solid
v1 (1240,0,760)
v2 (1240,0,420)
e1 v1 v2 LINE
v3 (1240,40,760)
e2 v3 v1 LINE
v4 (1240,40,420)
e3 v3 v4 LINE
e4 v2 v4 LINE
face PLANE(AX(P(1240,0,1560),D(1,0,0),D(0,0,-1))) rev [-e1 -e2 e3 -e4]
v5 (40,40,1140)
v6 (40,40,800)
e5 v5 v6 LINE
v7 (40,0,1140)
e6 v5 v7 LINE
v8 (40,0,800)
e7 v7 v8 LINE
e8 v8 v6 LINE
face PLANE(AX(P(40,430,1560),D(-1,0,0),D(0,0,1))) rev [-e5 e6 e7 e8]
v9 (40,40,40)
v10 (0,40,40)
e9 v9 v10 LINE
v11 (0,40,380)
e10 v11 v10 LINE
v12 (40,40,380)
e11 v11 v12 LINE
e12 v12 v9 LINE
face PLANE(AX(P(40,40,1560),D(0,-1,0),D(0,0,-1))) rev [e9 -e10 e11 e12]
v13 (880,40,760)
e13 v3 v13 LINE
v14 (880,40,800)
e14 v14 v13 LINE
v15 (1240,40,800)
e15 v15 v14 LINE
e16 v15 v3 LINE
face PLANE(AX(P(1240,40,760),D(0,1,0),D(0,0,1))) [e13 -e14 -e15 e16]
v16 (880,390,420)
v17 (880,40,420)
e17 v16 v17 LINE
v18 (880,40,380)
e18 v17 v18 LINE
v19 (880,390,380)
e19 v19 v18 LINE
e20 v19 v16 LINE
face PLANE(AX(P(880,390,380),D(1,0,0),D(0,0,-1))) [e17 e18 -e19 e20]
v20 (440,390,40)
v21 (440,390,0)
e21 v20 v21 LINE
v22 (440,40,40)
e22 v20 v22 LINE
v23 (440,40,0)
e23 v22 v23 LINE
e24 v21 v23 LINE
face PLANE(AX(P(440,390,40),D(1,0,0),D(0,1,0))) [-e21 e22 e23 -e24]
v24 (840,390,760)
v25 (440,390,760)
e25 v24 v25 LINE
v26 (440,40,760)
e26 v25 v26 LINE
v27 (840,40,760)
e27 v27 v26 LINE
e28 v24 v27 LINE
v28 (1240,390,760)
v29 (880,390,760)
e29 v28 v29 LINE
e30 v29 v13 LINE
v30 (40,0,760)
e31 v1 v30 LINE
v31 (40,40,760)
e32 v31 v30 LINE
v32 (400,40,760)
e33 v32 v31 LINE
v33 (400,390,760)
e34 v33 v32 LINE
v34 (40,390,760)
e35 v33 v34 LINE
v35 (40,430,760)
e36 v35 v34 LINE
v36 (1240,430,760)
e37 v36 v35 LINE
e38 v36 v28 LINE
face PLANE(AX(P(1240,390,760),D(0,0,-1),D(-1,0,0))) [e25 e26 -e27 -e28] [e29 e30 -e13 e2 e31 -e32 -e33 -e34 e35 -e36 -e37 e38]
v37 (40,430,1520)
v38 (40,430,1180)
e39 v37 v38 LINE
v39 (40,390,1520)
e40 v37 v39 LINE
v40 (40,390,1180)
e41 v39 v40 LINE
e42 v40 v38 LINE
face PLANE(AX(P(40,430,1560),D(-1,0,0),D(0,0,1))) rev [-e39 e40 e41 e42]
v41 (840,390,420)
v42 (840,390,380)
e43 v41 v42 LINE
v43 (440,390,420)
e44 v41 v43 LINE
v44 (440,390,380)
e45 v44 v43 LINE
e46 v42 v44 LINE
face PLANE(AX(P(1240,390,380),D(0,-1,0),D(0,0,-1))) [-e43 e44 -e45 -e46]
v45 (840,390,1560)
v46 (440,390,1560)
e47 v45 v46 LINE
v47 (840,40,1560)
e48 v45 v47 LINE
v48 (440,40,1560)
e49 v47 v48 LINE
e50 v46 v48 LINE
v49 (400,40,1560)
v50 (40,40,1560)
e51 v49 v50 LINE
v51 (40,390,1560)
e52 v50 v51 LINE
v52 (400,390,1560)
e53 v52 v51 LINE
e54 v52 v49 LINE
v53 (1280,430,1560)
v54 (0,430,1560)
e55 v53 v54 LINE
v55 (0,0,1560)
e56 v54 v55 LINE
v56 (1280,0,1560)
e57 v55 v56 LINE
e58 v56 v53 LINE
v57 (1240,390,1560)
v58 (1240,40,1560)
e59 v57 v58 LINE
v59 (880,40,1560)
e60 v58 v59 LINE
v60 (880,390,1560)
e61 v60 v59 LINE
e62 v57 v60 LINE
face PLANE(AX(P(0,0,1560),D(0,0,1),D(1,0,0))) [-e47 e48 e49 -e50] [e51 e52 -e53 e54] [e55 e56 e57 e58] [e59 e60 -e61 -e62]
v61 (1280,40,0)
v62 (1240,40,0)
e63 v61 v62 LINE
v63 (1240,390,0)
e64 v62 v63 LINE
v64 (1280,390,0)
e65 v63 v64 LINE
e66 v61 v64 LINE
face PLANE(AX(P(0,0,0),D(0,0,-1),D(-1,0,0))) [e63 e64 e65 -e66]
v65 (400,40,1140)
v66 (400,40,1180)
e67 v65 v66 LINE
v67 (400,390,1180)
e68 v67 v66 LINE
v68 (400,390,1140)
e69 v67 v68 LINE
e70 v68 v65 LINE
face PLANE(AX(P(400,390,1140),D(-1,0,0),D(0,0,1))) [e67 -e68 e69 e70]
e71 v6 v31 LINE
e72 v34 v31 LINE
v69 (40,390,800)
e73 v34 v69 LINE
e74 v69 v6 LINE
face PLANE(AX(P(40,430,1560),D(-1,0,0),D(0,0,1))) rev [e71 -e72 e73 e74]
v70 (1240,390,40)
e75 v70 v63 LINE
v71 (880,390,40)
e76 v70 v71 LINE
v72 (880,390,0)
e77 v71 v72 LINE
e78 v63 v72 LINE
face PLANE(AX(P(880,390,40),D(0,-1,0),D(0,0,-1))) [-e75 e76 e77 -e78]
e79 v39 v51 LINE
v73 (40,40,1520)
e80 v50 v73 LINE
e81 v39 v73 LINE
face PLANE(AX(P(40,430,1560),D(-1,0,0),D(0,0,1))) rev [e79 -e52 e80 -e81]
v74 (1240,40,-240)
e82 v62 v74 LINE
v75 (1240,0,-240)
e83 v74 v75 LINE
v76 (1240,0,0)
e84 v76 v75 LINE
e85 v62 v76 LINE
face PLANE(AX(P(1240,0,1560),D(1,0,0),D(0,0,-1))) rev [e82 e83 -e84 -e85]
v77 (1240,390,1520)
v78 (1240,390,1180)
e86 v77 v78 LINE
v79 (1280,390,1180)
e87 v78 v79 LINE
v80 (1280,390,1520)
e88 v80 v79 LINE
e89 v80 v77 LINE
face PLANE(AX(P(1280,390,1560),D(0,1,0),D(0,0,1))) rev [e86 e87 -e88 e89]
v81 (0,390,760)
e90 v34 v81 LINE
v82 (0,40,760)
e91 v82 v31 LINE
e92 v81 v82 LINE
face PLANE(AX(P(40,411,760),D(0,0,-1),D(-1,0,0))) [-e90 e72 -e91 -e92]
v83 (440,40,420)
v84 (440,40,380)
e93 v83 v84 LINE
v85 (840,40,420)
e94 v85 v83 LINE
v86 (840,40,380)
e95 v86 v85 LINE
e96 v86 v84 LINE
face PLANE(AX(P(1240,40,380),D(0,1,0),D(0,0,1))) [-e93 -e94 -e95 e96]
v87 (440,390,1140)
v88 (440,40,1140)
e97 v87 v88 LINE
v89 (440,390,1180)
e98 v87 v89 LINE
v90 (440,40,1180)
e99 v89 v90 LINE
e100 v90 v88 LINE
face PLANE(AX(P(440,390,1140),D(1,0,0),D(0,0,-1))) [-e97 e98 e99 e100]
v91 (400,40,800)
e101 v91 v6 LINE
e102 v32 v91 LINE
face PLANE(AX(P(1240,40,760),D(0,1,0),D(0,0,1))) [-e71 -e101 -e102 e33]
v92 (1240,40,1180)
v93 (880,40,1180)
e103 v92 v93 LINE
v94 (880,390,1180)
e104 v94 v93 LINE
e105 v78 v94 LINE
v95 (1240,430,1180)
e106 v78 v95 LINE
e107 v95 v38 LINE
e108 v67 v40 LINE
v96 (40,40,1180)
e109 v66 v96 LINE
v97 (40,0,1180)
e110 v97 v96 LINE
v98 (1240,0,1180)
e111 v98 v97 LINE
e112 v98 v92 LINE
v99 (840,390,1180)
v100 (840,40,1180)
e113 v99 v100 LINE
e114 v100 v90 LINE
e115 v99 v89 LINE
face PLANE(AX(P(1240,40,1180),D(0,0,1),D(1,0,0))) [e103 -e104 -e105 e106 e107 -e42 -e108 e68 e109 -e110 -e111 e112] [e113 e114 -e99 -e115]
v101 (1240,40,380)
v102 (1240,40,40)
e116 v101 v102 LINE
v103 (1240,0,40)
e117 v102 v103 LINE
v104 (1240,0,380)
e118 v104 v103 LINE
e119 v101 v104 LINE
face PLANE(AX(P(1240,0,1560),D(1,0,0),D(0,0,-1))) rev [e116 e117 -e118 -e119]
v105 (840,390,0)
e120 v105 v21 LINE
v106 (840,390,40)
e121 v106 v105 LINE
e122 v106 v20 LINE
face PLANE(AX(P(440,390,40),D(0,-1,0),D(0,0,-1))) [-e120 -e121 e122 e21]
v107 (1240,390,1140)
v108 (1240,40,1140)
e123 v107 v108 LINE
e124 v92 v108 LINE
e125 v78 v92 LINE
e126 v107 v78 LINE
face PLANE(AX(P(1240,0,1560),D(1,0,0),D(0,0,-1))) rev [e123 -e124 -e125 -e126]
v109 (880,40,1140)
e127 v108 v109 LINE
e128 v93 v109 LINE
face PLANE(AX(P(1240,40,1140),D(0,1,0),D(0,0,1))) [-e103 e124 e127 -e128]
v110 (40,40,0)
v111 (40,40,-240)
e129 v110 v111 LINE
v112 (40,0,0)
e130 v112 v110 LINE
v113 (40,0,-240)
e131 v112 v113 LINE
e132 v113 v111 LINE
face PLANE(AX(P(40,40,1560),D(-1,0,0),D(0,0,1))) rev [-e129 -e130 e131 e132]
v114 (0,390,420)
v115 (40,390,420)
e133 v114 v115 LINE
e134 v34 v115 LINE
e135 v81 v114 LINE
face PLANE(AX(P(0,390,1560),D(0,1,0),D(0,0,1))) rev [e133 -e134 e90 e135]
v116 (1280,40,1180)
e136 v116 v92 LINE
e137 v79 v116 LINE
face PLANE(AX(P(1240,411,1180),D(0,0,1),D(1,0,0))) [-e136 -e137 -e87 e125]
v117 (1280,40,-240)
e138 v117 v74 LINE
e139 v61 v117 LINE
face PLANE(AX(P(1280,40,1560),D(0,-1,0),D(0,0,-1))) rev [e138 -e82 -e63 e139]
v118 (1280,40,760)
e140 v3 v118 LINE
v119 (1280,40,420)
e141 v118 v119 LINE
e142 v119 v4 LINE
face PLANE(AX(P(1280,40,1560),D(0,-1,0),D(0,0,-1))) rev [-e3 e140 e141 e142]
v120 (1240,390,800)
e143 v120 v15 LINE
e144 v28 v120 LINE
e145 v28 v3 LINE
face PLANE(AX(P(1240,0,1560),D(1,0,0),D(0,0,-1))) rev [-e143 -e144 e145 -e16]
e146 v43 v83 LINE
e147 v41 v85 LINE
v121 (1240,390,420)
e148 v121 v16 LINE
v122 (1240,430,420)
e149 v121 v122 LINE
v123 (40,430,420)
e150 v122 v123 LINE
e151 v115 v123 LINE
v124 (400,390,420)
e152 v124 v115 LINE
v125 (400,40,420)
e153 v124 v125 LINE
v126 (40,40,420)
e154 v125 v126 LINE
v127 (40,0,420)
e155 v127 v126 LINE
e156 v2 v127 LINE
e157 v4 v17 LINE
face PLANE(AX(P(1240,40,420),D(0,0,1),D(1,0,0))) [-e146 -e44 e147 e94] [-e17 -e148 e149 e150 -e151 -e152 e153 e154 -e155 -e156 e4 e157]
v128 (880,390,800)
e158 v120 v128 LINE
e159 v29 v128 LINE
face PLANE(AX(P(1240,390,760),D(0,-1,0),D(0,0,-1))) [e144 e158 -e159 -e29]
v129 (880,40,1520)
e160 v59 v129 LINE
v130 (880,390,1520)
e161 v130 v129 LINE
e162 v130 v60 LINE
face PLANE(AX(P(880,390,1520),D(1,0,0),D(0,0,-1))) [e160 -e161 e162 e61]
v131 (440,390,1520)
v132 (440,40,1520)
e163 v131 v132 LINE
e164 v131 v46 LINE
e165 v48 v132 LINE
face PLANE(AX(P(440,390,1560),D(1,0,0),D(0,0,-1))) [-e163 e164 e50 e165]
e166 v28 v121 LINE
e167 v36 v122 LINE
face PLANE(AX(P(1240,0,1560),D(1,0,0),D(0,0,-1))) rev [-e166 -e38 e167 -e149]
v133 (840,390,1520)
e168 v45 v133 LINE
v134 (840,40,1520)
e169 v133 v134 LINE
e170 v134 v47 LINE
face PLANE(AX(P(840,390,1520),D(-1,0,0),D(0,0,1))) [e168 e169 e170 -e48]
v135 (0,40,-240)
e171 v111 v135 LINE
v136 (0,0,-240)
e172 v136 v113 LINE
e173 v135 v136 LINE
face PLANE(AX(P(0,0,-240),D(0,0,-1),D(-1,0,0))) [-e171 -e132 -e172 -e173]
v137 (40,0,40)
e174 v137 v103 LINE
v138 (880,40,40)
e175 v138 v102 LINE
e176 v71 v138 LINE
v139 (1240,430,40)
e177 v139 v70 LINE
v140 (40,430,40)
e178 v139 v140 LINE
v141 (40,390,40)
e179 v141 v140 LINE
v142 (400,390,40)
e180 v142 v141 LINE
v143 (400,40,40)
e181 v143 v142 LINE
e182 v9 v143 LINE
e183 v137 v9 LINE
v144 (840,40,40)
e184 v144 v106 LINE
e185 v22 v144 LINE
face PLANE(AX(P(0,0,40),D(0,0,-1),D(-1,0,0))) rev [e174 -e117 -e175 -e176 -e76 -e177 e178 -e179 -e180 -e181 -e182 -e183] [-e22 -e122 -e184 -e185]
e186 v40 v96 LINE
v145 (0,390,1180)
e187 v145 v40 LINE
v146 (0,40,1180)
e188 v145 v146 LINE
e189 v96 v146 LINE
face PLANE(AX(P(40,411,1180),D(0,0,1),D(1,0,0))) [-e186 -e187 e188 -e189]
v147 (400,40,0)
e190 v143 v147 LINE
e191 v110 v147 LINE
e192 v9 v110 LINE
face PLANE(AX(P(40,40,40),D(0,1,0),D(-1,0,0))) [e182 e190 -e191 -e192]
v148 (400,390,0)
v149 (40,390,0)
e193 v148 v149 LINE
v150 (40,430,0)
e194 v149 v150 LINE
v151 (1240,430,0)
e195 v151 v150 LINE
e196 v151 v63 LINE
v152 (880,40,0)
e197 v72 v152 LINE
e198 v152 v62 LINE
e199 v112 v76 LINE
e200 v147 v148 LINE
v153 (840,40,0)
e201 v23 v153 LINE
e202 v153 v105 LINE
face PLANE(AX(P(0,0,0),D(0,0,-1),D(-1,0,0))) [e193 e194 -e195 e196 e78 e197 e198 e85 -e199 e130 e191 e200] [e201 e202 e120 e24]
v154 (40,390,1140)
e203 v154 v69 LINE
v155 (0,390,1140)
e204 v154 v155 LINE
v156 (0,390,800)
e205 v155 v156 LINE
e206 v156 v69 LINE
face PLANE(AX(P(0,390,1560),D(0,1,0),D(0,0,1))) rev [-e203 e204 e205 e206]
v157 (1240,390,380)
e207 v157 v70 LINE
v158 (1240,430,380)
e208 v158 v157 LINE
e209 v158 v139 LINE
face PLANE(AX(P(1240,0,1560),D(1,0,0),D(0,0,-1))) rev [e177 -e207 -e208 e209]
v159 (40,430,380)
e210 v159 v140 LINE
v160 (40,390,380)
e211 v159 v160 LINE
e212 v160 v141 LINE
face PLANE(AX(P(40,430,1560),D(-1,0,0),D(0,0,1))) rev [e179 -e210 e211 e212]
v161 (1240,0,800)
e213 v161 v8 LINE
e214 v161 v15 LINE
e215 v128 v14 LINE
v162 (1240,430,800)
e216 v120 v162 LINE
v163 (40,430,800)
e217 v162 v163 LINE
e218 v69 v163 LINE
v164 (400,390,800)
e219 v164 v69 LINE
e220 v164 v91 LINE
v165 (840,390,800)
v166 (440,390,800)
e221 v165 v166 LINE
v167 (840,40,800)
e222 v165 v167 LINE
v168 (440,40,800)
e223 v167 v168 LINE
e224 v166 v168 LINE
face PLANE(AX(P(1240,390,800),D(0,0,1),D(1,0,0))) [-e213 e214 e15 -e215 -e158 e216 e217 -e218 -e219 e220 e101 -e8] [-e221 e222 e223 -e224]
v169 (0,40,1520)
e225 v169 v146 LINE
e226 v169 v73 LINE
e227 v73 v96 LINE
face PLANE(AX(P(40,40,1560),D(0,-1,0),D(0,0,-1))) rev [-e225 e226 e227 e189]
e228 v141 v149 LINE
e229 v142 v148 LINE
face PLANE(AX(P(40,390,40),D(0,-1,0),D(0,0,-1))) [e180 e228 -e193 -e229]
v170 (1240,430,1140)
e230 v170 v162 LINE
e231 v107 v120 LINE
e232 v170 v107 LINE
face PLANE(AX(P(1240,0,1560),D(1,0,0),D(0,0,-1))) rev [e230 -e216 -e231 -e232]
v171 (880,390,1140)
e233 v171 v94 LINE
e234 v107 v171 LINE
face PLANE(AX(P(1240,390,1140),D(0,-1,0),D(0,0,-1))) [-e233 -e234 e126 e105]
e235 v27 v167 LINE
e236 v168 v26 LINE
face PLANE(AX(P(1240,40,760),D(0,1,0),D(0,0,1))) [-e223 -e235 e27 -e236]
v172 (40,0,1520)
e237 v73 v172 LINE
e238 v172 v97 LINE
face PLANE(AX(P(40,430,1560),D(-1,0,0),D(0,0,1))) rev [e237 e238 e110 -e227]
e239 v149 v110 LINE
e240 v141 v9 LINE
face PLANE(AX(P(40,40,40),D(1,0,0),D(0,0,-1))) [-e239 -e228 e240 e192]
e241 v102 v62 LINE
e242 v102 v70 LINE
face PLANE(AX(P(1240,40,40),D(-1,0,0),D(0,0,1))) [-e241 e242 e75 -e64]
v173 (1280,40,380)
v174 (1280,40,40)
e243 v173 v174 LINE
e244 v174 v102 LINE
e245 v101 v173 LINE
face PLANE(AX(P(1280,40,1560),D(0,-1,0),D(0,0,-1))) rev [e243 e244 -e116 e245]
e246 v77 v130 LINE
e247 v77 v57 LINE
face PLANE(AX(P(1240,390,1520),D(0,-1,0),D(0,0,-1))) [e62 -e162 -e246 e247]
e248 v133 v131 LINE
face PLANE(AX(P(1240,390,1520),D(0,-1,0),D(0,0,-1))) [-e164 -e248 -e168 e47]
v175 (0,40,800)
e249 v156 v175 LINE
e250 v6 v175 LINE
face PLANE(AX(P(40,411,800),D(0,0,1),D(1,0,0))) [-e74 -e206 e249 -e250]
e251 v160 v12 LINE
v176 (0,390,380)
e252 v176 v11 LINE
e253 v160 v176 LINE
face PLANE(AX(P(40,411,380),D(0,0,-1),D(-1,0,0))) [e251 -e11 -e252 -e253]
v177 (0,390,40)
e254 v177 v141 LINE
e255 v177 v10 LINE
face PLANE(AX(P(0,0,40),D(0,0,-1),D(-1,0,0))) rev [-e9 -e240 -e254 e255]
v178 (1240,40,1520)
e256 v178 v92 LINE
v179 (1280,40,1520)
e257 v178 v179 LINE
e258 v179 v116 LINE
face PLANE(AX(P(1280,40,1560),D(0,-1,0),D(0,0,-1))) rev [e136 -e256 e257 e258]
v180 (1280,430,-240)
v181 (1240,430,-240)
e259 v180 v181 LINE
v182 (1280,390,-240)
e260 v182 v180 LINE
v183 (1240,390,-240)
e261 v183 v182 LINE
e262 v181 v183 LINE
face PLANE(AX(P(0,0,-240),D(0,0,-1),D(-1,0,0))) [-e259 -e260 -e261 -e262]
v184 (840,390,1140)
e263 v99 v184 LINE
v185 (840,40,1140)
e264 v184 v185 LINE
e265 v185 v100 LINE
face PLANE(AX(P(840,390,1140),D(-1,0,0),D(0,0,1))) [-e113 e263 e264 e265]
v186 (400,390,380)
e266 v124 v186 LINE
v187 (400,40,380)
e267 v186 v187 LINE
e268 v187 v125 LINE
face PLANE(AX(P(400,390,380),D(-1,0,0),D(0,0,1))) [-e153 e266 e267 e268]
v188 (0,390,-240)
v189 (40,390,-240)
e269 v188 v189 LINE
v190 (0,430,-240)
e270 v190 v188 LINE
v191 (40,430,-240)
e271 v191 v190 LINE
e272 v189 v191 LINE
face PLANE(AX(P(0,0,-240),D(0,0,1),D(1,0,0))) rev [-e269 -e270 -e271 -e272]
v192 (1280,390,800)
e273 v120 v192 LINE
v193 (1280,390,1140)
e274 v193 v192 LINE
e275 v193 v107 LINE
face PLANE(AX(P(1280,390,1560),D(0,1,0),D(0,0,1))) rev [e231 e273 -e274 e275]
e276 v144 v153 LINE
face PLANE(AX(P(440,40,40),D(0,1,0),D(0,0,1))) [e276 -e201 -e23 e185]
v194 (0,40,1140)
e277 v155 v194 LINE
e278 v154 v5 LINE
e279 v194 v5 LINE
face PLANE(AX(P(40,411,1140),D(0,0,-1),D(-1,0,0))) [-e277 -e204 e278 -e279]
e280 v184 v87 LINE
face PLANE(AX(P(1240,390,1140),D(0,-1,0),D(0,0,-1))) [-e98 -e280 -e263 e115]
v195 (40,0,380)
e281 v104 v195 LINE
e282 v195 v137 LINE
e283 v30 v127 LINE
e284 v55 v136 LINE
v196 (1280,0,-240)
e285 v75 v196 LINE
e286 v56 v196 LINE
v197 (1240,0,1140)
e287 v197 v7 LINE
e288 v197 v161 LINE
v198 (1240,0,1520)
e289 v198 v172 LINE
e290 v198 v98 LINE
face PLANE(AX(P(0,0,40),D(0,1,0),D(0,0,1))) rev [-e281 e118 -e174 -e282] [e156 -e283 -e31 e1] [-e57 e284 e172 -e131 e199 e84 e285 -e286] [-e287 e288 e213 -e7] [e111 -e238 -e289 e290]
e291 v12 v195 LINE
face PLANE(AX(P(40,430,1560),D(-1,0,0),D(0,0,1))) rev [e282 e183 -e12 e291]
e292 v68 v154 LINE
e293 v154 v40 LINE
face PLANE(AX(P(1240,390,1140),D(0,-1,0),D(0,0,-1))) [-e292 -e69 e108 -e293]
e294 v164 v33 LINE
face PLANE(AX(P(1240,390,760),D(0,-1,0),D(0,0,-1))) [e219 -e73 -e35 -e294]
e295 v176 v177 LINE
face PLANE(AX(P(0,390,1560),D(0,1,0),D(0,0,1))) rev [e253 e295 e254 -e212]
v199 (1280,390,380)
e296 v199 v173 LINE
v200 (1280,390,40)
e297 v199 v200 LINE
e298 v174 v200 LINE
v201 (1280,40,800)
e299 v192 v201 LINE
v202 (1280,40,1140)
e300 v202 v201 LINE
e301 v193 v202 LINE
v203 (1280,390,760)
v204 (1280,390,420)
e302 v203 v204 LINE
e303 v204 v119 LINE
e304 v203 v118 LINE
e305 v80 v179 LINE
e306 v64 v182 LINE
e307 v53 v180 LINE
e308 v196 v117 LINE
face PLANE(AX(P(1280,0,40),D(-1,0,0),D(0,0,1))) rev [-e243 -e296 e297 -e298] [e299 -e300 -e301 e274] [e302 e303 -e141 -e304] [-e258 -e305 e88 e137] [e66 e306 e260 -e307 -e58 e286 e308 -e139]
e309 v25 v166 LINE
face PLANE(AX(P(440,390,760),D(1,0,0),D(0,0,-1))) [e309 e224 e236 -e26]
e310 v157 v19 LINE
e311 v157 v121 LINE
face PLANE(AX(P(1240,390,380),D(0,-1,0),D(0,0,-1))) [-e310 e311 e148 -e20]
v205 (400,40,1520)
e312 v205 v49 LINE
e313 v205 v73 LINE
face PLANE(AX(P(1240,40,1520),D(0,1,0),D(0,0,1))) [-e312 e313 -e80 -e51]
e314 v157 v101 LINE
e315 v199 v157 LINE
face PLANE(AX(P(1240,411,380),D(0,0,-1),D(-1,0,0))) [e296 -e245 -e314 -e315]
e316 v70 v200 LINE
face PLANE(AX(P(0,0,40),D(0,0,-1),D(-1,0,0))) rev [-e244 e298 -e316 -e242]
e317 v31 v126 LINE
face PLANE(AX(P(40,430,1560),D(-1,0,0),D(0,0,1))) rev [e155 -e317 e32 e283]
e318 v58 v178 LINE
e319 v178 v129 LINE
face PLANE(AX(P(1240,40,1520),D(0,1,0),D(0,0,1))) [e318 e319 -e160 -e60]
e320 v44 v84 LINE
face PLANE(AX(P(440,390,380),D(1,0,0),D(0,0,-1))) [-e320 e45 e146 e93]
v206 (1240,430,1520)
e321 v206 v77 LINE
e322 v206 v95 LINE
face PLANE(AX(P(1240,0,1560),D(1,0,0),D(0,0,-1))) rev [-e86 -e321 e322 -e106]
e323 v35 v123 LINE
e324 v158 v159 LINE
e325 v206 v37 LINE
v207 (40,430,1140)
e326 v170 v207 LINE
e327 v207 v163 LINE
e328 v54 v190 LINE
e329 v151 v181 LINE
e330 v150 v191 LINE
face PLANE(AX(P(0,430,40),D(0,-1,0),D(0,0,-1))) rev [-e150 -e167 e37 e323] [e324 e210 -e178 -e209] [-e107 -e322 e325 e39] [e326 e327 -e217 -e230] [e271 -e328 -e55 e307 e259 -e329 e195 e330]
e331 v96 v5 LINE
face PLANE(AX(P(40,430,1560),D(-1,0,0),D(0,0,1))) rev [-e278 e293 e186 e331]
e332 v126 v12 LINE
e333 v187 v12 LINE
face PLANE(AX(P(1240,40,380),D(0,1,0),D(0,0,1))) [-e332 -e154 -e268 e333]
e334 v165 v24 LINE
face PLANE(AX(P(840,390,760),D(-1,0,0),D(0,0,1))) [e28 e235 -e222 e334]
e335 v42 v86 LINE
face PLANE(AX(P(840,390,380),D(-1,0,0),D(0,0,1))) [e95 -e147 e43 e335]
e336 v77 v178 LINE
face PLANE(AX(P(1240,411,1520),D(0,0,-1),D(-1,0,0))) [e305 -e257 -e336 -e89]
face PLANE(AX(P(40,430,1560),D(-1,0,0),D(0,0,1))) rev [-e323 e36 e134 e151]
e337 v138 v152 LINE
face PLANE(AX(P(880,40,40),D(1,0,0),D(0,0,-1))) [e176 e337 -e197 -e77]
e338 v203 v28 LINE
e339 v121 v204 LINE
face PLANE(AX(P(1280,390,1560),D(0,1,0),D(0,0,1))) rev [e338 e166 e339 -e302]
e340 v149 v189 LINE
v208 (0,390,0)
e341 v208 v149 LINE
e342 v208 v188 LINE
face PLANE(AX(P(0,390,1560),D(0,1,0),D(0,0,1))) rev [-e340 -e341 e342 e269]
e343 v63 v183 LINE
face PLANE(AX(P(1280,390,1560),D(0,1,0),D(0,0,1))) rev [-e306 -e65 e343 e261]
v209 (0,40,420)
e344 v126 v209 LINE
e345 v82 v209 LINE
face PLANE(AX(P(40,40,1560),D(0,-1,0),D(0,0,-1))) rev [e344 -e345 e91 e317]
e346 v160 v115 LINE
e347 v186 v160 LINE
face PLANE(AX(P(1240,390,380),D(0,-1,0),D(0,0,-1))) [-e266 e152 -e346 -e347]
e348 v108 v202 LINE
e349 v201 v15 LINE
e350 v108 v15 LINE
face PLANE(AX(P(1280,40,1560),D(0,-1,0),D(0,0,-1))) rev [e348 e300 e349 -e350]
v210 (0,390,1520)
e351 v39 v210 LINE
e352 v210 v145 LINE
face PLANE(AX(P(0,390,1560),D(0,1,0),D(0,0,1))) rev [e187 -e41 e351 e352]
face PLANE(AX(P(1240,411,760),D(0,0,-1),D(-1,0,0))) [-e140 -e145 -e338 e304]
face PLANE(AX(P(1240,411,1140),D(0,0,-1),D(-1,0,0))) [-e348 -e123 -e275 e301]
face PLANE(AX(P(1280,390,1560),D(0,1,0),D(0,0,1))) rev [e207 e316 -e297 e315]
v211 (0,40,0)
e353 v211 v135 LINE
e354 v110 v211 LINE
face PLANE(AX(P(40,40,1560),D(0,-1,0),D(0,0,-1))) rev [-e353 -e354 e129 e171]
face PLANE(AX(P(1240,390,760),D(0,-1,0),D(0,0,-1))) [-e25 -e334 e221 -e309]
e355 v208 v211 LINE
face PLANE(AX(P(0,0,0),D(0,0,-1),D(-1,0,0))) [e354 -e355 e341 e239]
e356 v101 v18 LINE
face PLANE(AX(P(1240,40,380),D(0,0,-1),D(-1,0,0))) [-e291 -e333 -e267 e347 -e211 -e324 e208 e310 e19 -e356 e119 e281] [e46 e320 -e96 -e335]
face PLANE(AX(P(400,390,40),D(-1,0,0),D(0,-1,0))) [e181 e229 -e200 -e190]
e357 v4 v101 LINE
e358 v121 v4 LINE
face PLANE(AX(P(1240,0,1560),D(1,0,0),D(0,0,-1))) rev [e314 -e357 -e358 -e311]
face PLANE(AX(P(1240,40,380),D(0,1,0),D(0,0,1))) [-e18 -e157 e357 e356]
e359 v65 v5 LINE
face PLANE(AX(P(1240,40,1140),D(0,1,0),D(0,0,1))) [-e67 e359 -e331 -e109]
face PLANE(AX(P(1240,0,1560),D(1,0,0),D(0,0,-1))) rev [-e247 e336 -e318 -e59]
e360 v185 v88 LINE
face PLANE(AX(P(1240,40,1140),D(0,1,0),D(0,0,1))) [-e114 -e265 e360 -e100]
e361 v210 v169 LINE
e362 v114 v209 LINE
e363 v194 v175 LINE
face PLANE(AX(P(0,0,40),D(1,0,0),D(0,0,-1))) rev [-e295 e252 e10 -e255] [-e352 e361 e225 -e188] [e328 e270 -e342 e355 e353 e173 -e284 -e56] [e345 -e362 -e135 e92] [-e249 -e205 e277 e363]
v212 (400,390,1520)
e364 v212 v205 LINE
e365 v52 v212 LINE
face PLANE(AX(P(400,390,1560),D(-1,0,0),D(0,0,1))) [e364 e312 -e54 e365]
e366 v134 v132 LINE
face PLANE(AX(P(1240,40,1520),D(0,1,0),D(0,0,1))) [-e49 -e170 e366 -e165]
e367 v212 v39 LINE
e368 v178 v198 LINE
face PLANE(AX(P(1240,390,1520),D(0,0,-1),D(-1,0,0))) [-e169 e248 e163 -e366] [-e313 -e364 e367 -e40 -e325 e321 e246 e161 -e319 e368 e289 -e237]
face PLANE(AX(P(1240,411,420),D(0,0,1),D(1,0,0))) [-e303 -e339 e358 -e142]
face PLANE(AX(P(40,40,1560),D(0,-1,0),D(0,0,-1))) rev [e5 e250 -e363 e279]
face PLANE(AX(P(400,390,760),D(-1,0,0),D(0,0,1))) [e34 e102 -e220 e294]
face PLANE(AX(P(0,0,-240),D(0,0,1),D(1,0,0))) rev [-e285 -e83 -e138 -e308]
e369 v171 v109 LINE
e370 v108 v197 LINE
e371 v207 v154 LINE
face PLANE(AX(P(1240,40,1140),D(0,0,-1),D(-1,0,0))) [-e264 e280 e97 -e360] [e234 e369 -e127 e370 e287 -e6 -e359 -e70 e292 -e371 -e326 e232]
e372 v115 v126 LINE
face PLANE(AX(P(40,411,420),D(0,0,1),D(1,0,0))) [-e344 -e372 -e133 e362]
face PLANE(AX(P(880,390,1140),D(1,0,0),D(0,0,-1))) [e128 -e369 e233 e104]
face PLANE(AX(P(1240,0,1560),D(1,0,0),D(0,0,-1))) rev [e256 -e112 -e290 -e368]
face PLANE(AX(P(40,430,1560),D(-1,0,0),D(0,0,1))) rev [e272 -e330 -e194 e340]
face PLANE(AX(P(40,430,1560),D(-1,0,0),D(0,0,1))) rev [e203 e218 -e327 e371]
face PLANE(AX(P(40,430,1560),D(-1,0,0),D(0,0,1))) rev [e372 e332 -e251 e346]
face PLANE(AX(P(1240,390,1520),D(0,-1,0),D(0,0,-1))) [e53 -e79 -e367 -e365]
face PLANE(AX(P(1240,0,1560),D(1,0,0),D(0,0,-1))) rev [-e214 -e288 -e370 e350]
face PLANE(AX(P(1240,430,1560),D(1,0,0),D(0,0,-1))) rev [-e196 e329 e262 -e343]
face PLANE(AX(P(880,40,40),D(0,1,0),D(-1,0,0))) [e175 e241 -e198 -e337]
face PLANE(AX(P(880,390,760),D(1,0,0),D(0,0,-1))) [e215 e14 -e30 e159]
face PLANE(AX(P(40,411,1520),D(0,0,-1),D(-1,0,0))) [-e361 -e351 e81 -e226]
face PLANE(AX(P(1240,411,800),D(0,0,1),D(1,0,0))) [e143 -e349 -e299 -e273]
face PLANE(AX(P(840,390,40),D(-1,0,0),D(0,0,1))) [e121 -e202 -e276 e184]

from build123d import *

# Parameters (mm, degrees)
SKETCH1_W                = 1280
SKETCH1_H                = 430
SKETCH1_W_2              = 360
SKETCH1_H_2              = 350
SKETCH1_W_3              = 400
BOSS_EXTRUDE1_DEPTH      = 40
BOSS_EXTRUDE2_DEPTH      = 1520
BOSS_EXTRUDE2_DEPTH_BACK = 280
SKETCH2_W                = 40
SKETCH2_H                = 40
SKETCH3_W                = 40
SKETCH3_H                = 40
BOSS_EXTRUDE3_DEPTH      = 411
SKETCH4_W                = 40
SKETCH4_H                = 40
BOSS_EXTRUDE4_DEPTH      = 1240
SKETCH5_W                = 40
SKETCH5_H                = 40
BOSS_EXTRUDE5_DEPTH      = 390


with BuildPart() as part:
    # Sketch1 → Boss-Extrude1 (new body)
    with BuildSketch(Plane.XY):
        with Locations((640, 215)):
            Rectangle(SKETCH1_W, SKETCH1_H)
        with Locations((220, 215)):
            Rectangle(SKETCH1_W_2, SKETCH1_H_2, mode=Mode.SUBTRACT)
        with Locations((1060, 215)):
            Rectangle(SKETCH1_W_2, SKETCH1_H_2, mode=Mode.SUBTRACT)
        with Locations((640, 215)):
            Rectangle(SKETCH1_W_3, SKETCH1_H_2, mode=Mode.SUBTRACT)
    extrude(amount=BOSS_EXTRUDE1_DEPTH)

    # Sketch2 → Boss-Extrude2 (add, two sides: drawn at the far end of the back side and taken through both)
    with BuildSketch(Plane.XY.offset(40).offset(-BOSS_EXTRUDE2_DEPTH_BACK)):
        with Locations((20, 410)):
            Rectangle(SKETCH2_W, SKETCH2_H)
        with Locations((20, 20)):
            Rectangle(SKETCH2_W, SKETCH2_H)
        with Locations((1260, 20)):
            Rectangle(SKETCH2_W, SKETCH2_H)
        with Locations((1260, 410)):
            Rectangle(SKETCH2_W, SKETCH2_H)
    extrude(amount=BOSS_EXTRUDE2_DEPTH + BOSS_EXTRUDE2_DEPTH_BACK)

    # Sketch3 → Boss-Extrude3 (add)
    with BuildSketch(Plane.XZ):
        with Locations((20, 400)):
            Rectangle(SKETCH3_W, SKETCH3_H)
        with Locations((1260, 400)):
            Rectangle(SKETCH3_W, SKETCH3_H)
        with Locations((20, 780)):
            Rectangle(SKETCH3_W, SKETCH3_H)
        with Locations((1260, 780)):
            Rectangle(SKETCH3_W, SKETCH3_H)
        with Locations((20, 1160)):
            Rectangle(SKETCH3_W, SKETCH3_H)
        with Locations((1260, 1160)):
            Rectangle(SKETCH3_W, SKETCH3_H)
        with Locations((20, 1540)):
            Rectangle(SKETCH3_W, SKETCH3_H)
        with Locations((1260, 1540)):
            Rectangle(SKETCH3_W, SKETCH3_H)
    extrude(amount=-BOSS_EXTRUDE3_DEPTH)

    # Sketch4 → Boss-Extrude4 (add)
    with BuildSketch(Plane.ZY):
        with Locations((20, 410)):
            Rectangle(SKETCH4_W, SKETCH4_H)
        with Locations((20, 20)):
            Rectangle(SKETCH4_W, SKETCH4_H)
        with Locations((400, 20)):
            Rectangle(SKETCH4_W, SKETCH4_H)
        with Locations((400, 410)):
            Rectangle(SKETCH4_W, SKETCH4_H)
        with Locations((780, 410)):
            Rectangle(SKETCH4_W, SKETCH4_H)
        with Locations((780, 20)):
            Rectangle(SKETCH4_W, SKETCH4_H)
        with Locations((1160, 20)):
            Rectangle(SKETCH4_W, SKETCH4_H)
        with Locations((1160, 410)):
            Rectangle(SKETCH4_W, SKETCH4_H)
        with Locations((1540, 410)):
            Rectangle(SKETCH4_W, SKETCH4_H)
        with Locations((1540, 20)):
            Rectangle(SKETCH4_W, SKETCH4_H)
    extrude(amount=-BOSS_EXTRUDE4_DEPTH)

    # Sketch5 → Boss-Extrude5 (add)
    with BuildSketch(Plane.XZ):
        with Locations((420, 20)):
            Rectangle(SKETCH5_W, SKETCH5_H)
        with Locations((860, 20)):
            Rectangle(SKETCH5_W, SKETCH5_H)
        with Locations((420, 400)):
            Rectangle(SKETCH5_W, SKETCH5_H)
        with Locations((860, 400)):
            Rectangle(SKETCH5_W, SKETCH5_H)
        with Locations((420, 780)):
            Rectangle(SKETCH5_W, SKETCH5_H)
        with Locations((860, 780)):
            Rectangle(SKETCH5_W, SKETCH5_H)
        with Locations((420, 1160)):
            Rectangle(SKETCH5_W, SKETCH5_H)
        with Locations((860, 1160)):
            Rectangle(SKETCH5_W, SKETCH5_H)
        with Locations((860, 1540)):
            Rectangle(SKETCH5_W, SKETCH5_H)
        with Locations((420, 1540)):
            Rectangle(SKETCH5_W, SKETCH5_H)
    extrude(amount=-BOSS_EXTRUDE5_DEPTH)


solid = part.part
